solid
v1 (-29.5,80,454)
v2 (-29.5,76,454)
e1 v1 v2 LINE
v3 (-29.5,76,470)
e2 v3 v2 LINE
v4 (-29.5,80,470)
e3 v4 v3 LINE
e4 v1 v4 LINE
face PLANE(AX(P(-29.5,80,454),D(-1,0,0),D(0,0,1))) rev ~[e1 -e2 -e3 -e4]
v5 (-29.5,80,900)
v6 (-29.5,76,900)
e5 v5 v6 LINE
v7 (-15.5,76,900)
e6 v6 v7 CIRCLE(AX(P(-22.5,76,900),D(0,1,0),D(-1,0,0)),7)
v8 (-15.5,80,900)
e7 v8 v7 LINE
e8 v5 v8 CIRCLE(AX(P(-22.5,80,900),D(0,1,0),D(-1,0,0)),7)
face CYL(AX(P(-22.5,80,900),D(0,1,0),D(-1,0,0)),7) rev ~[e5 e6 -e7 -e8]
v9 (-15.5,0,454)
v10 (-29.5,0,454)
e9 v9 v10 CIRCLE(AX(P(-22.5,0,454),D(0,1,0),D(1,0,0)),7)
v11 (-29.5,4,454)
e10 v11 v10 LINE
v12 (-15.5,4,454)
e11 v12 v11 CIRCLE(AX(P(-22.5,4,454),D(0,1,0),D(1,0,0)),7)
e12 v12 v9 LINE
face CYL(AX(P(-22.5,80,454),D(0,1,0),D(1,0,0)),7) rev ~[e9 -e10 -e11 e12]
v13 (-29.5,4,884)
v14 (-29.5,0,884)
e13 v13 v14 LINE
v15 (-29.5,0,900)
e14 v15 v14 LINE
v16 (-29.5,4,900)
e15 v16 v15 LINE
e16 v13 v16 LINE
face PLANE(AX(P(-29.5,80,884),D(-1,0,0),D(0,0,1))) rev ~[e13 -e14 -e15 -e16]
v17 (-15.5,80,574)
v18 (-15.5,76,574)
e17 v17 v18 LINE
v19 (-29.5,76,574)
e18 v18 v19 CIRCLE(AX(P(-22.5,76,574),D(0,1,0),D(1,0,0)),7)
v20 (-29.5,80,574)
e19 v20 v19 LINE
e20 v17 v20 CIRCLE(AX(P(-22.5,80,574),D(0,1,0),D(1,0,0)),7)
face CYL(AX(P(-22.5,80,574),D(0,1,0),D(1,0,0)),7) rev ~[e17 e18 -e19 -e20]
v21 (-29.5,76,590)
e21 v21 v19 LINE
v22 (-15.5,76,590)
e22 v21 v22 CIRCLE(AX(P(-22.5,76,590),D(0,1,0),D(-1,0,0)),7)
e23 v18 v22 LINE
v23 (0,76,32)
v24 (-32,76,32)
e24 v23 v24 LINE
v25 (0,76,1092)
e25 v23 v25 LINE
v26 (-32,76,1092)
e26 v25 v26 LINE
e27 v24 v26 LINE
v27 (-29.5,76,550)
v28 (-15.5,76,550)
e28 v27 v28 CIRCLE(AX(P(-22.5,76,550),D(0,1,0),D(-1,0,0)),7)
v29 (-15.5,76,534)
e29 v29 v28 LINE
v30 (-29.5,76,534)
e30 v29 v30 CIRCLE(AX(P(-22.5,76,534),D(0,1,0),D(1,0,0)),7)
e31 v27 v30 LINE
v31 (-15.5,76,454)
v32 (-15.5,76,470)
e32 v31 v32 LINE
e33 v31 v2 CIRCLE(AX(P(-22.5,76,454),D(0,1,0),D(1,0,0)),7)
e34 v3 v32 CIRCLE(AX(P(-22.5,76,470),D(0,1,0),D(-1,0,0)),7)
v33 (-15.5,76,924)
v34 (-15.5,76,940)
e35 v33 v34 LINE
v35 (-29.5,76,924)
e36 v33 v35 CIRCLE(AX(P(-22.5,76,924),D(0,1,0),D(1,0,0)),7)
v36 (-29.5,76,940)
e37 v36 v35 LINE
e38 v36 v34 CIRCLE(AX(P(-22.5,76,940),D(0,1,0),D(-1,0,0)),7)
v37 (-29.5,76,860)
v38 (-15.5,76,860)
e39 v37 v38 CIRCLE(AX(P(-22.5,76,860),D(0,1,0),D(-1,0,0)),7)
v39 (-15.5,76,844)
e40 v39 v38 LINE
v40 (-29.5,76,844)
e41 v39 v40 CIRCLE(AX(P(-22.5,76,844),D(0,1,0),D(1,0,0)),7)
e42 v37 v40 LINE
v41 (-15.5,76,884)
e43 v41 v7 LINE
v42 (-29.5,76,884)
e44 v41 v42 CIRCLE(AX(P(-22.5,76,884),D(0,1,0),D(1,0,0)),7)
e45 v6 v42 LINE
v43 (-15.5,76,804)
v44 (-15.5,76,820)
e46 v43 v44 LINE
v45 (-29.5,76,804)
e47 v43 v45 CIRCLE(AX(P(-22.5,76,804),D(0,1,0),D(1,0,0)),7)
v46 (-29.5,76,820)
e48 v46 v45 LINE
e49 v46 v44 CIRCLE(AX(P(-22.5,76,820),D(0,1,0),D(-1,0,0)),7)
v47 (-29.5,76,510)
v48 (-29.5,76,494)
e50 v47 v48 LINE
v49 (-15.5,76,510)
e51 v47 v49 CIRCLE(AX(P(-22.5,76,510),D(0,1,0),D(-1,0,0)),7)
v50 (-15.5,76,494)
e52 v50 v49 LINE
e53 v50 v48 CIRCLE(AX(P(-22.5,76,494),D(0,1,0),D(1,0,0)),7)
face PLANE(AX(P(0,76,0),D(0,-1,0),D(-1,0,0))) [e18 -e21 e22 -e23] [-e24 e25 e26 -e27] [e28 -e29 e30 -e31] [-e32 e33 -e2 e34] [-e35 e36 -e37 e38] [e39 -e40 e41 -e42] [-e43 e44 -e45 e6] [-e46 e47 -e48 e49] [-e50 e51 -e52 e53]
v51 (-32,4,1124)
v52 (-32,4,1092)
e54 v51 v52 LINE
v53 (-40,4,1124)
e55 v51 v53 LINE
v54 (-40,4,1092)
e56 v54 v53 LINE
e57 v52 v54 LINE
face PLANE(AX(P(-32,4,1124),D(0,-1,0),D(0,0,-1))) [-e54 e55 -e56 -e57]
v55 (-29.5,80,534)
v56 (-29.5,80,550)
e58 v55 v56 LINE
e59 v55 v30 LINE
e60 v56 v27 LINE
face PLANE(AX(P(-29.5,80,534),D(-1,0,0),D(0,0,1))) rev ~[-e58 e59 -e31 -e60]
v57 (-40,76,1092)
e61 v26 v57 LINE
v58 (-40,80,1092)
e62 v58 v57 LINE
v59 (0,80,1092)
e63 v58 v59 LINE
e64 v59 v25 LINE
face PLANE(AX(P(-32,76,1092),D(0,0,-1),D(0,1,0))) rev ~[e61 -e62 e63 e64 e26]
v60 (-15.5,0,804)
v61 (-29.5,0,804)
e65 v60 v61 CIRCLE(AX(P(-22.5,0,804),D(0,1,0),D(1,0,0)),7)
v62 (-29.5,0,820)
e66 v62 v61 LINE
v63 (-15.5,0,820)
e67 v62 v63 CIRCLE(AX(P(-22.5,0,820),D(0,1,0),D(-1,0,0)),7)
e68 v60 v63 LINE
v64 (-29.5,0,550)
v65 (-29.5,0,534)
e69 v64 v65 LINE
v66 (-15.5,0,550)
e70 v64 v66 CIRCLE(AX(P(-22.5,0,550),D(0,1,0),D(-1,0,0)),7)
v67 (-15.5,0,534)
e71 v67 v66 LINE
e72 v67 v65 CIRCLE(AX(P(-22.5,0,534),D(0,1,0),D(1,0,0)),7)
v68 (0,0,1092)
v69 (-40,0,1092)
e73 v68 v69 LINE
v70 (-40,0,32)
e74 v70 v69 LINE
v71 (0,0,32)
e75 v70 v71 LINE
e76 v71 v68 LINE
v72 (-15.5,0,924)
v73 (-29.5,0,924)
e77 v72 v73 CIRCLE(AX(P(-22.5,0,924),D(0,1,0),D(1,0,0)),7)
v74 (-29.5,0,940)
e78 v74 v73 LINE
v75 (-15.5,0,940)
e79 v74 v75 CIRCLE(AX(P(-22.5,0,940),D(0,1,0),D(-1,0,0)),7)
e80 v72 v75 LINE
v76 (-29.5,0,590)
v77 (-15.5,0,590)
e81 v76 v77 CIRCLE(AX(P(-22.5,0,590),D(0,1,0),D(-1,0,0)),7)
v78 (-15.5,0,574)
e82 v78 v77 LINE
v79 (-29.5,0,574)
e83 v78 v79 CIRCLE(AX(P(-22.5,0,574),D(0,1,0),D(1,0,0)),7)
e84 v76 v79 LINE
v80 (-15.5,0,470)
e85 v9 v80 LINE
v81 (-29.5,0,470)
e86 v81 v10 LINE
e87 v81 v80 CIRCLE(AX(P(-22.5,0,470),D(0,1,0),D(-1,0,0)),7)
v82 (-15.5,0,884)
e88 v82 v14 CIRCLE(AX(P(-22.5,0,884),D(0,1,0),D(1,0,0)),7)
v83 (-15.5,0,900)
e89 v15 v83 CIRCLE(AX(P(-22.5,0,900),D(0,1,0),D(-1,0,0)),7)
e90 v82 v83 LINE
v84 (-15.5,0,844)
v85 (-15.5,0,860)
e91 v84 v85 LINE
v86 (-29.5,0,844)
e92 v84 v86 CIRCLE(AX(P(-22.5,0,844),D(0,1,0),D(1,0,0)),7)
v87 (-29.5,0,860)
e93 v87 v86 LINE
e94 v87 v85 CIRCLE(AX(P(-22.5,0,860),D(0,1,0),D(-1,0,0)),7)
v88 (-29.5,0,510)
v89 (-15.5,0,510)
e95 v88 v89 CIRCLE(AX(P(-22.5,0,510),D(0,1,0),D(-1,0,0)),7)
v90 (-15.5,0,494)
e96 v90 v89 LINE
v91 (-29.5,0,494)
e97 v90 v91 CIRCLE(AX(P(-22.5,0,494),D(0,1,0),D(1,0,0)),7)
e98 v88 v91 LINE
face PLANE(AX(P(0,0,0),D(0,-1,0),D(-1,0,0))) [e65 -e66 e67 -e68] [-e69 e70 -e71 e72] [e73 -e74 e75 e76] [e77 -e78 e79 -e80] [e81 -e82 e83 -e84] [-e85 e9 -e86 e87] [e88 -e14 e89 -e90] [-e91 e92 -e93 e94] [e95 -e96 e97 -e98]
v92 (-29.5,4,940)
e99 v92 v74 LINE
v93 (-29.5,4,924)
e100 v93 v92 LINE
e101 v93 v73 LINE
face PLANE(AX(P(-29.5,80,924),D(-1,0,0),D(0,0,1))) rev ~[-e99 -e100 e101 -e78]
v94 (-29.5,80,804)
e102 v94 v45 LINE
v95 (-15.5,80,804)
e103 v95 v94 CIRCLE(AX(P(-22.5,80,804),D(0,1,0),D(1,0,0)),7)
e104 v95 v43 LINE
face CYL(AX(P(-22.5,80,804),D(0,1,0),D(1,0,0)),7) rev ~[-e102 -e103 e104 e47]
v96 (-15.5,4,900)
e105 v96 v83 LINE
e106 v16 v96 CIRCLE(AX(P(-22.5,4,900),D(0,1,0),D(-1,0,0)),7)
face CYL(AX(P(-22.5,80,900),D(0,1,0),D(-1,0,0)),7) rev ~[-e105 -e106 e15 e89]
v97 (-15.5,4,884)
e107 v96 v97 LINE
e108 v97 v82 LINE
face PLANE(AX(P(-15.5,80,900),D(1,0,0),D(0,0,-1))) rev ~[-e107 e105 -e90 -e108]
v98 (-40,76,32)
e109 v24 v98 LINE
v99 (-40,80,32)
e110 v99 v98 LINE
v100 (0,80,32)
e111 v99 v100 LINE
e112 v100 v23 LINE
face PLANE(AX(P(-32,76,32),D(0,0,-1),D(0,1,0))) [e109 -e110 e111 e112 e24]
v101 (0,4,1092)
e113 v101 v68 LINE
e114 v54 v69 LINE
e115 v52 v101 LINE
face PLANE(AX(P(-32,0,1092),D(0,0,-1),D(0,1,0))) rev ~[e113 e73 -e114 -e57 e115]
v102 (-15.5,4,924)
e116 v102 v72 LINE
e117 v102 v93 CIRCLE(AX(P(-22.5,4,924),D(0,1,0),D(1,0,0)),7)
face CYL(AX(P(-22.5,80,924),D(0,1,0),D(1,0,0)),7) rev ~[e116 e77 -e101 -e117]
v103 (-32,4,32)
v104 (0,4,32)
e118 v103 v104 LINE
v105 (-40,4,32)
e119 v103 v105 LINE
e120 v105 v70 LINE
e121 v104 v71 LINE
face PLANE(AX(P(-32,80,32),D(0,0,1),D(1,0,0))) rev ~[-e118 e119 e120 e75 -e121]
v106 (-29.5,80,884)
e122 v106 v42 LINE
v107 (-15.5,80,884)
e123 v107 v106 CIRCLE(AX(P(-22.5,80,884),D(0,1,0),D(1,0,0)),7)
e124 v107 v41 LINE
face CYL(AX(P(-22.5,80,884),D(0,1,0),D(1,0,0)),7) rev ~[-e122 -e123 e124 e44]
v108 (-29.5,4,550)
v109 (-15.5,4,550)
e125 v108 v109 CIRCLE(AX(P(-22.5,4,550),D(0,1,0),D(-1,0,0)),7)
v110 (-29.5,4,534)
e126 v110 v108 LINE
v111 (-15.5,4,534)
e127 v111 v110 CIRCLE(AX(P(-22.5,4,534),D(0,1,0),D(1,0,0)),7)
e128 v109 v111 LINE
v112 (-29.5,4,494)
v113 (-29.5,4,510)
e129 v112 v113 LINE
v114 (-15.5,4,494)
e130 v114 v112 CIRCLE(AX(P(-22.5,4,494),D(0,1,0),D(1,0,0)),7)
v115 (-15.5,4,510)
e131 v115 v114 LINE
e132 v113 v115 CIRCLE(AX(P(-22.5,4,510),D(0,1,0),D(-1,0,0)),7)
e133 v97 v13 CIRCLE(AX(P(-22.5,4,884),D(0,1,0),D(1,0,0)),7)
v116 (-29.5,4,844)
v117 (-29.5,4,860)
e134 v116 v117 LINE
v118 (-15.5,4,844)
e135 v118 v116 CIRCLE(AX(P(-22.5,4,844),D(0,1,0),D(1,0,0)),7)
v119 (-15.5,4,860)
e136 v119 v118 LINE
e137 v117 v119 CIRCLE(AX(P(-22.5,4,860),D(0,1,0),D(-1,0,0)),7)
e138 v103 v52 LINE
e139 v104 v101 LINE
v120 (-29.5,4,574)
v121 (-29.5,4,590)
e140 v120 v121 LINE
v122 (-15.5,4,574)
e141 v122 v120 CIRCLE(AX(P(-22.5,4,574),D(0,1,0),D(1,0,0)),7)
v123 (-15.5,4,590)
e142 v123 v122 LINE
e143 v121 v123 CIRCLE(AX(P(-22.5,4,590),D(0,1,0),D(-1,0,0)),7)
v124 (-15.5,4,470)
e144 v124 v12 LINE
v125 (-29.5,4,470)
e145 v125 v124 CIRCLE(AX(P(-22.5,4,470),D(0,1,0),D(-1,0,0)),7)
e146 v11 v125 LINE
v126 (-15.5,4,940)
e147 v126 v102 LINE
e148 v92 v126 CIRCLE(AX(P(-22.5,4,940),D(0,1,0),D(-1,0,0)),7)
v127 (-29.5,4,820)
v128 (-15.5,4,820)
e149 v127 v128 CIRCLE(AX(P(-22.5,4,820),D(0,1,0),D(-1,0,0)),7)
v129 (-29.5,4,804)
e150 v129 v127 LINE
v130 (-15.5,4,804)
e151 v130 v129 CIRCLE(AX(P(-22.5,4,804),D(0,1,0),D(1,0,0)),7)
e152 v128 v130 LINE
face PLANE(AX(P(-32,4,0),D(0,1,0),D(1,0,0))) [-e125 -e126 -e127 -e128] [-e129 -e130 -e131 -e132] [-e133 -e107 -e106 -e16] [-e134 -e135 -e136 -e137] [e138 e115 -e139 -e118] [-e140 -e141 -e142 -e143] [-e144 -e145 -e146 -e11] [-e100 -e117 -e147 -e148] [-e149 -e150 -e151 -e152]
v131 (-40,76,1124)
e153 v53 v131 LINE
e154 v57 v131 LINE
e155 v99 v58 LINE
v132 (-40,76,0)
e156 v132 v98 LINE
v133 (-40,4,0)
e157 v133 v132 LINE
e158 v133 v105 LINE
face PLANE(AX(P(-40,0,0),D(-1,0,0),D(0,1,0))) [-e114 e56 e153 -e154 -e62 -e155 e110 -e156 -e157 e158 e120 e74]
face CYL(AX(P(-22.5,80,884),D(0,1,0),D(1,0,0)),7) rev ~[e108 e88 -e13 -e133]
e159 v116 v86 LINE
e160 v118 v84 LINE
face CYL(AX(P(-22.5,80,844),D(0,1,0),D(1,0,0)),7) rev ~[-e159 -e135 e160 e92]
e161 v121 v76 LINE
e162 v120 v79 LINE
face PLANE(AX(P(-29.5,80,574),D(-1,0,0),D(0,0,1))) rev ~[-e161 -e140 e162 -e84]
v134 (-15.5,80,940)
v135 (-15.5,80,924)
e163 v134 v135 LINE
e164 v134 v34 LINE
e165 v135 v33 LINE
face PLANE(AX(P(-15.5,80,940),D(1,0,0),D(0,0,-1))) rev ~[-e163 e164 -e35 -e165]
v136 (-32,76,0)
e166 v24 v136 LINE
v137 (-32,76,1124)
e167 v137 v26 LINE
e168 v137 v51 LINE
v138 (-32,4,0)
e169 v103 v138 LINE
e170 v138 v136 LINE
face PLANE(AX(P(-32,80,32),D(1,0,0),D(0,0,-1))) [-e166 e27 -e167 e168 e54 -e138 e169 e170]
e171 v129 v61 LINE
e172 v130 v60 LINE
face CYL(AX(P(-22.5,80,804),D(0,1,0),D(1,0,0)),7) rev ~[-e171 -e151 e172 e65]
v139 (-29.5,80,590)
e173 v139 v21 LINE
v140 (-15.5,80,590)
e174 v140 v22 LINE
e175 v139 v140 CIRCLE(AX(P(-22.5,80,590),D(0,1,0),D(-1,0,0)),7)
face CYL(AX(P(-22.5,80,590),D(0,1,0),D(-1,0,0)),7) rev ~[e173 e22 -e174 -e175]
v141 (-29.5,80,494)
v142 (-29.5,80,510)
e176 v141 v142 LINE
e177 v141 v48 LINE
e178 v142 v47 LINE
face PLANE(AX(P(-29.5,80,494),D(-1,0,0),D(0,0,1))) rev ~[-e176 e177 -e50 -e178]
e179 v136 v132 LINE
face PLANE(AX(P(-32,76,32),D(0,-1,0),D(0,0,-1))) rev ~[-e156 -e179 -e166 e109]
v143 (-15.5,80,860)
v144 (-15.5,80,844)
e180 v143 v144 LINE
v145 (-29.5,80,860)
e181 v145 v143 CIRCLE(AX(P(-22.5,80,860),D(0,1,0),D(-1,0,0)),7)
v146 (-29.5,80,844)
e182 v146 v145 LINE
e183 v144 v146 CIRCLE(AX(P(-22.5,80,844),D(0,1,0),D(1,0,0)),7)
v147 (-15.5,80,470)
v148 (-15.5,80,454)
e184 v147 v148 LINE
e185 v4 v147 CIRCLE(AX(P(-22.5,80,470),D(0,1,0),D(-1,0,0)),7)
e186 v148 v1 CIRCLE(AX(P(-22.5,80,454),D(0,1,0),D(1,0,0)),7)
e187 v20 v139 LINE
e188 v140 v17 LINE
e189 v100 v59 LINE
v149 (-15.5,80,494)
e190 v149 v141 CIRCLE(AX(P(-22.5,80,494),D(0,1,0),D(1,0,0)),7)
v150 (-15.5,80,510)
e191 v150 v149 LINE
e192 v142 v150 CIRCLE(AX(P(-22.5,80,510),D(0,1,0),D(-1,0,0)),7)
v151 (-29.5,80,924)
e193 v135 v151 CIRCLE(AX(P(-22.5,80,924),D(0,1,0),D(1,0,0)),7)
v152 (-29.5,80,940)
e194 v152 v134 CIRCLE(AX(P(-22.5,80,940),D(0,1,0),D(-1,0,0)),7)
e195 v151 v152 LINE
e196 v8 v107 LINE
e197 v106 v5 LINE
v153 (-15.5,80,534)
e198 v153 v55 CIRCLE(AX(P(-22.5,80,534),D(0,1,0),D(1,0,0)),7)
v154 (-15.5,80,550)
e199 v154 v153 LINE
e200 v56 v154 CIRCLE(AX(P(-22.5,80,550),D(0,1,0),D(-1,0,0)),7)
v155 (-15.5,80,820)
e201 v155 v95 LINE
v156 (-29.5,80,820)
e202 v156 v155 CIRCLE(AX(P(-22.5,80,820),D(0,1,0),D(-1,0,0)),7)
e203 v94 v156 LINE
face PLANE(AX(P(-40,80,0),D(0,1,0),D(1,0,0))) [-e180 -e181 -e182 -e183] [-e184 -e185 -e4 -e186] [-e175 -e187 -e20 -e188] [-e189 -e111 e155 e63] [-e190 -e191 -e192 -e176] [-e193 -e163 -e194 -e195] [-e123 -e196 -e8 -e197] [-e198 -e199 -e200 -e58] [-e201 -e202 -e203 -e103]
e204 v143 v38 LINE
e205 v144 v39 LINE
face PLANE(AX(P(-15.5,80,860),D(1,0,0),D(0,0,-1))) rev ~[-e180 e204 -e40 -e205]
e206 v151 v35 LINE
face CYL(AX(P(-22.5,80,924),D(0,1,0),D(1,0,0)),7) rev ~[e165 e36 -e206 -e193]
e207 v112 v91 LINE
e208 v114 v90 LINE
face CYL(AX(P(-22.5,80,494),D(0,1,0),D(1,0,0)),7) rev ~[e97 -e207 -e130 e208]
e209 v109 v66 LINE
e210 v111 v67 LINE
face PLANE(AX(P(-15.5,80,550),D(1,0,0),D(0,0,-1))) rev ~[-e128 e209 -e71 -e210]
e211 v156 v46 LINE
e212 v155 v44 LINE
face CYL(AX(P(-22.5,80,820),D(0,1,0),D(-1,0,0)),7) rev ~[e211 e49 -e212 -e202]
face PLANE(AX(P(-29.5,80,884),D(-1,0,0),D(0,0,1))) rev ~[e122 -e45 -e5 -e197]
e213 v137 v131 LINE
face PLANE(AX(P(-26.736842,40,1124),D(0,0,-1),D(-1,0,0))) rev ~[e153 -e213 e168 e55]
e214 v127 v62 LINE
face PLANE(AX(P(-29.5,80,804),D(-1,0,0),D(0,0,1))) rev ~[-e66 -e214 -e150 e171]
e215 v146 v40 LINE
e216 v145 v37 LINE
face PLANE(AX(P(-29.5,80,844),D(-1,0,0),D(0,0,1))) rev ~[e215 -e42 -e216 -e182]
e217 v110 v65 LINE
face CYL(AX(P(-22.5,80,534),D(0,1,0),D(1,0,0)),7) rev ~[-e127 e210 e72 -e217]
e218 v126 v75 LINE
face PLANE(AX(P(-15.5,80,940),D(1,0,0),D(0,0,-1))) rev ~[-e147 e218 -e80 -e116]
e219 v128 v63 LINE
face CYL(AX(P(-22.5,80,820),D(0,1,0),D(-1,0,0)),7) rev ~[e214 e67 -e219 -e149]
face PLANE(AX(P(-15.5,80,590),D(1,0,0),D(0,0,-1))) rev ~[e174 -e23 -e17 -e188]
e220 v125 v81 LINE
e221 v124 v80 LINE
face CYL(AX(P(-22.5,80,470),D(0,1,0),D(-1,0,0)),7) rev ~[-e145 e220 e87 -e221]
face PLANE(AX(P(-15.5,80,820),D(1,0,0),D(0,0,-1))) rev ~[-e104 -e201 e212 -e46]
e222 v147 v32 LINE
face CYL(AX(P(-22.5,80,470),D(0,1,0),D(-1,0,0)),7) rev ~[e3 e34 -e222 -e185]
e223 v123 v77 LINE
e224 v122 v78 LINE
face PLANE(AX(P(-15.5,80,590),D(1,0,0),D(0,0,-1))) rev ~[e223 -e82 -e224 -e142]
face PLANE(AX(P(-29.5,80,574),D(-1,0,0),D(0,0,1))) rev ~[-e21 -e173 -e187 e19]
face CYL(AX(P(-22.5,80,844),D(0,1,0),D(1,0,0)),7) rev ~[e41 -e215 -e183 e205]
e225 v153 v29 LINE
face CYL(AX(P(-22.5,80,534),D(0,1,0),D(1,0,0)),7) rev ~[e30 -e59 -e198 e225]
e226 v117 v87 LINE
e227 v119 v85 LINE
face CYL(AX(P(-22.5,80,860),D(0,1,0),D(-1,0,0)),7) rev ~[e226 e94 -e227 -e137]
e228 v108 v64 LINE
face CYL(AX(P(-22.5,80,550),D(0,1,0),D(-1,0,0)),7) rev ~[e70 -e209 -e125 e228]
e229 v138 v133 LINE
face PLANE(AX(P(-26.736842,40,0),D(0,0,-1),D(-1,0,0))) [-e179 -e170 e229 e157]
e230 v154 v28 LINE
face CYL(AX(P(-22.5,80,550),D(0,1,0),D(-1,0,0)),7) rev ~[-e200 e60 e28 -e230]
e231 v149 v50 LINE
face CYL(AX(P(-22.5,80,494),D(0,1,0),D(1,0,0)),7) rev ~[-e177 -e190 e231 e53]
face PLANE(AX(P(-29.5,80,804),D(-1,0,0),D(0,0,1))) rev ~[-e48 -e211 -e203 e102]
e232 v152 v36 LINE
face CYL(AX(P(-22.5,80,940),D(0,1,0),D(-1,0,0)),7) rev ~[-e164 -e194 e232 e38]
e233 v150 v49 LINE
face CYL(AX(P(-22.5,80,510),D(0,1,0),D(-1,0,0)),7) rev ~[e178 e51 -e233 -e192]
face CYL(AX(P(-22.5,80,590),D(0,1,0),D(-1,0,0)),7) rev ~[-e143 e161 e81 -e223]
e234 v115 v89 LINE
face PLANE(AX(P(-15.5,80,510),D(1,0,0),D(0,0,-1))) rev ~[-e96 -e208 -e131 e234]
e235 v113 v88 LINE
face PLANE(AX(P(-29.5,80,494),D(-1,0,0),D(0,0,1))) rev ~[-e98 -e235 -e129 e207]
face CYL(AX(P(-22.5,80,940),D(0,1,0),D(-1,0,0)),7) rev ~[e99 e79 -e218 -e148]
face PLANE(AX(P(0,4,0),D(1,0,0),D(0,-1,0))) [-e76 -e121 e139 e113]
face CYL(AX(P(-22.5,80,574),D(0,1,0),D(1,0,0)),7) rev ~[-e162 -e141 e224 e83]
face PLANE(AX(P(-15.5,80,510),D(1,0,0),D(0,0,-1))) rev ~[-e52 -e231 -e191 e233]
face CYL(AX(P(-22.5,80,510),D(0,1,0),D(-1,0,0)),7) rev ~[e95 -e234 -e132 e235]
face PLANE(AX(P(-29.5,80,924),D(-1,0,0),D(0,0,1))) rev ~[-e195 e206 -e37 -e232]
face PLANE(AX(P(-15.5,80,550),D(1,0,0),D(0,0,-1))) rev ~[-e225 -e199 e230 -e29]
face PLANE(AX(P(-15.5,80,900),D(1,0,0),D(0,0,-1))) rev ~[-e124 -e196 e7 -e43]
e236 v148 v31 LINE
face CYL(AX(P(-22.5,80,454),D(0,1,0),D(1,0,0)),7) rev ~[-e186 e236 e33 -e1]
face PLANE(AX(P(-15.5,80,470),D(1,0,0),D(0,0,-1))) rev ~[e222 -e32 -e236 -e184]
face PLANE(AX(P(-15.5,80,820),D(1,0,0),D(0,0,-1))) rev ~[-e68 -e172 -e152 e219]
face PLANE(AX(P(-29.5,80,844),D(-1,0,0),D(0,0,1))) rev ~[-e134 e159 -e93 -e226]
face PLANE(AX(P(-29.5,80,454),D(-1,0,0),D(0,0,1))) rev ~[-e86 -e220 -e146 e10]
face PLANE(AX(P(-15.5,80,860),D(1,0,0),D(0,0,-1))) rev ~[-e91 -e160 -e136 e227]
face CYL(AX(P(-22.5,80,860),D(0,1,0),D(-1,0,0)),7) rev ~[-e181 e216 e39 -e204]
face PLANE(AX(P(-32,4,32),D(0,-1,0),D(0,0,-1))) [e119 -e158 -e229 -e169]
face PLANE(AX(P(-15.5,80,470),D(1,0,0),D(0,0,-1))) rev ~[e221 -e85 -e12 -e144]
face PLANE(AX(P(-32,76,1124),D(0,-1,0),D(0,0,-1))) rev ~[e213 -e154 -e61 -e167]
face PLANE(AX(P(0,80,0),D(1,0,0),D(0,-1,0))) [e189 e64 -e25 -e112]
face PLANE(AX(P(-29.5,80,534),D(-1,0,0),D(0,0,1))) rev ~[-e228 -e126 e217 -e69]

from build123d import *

# Parameters (mm, degrees)
EXTRUDE1_DEPTH         = 1124
SKETCH2_W              = 32
SKETCH2_H              = 32
CUT_EXTRUDE1_DEPTH     = 1128.553102962
SKETCH3_W              = 32
SKETCH3_H              = 4
CUT_EXTRUDE2_DEPTH     = 1200
CUT_EXTRUDE3_DEPTH     = 1128.553102962
LPATTERN1_COUNT        = 4
LPATTERN1_PITCH        = 40
LPATTERN2_COUNT        = 2
LPATTERN2_PITCH        = 350
LPATTERN2_COPY_1_DEPTH = 1128.553102962
LPATTERN2_COPY_2_DEPTH = 1128.553102962
LPATTERN2_COPY_3_DEPTH = 1128.553102962


with BuildPart() as part:
    # Sketch1 → Extrude1 (new body)
    with BuildSketch(Plane.XY):
        Polygon((0, 0), (-40, 0), (-40, 80), (0, 80), (0, 76), (-32, 76), (-32, 4), (0, 4), align=None)
    extrude(amount=EXTRUDE1_DEPTH)

    # Sketch2 → Cut-Extrude1 (cut, through all)
    with BuildSketch(Plane(origin=(0, 80, 0), x_dir=(1, 0, 0), z_dir=(0, 1, 0))):
        with Locations((-16, -16)):
            Rectangle(SKETCH2_W, SKETCH2_H)
        with Locations((-16, -1108)):
            Rectangle(SKETCH2_W, SKETCH2_H)
    extrude(amount=-CUT_EXTRUDE1_DEPTH, mode=Mode.SUBTRACT)

    # Sketch3 → Cut-Extrude2 (cut)
    with BuildSketch(Plane(origin=(-32, 0, 0), x_dir=(0, 0, -1), z_dir=(1, 0, 0))):
        with Locations((-1108, 78)):
            Rectangle(SKETCH3_W, SKETCH3_H)
        with Locations((-1108, 2)):
            Rectangle(SKETCH3_W, SKETCH3_H)
        with Locations((-16, 78)):
            Rectangle(SKETCH3_W, SKETCH3_H)
        with Locations((-16, 2)):
            Rectangle(SKETCH3_W, SKETCH3_H)
    extrude(amount=-CUT_EXTRUDE2_DEPTH, mode=Mode.SUBTRACT)

    # Sketch4 → Cut-Extrude3 (cut, through all)
    with BuildSketch(Plane(origin=(0, 80, 0), x_dir=(1, 0, 0), z_dir=(0, 1, 0))):
        with BuildLine():
            Line((-29.5, -924), (-29.5, -940))
            ThreePointArc((-29.5, -940), (-22.5, -947), (-15.5, -940))
            Line((-15.5, -940), (-15.5, -924))
            ThreePointArc((-15.5, -924), (-22.5, -917), (-29.5, -924))
        make_face()
    cut_extrude3 = extrude(amount=-CUT_EXTRUDE3_DEPTH, mode=Mode.SUBTRACT)

    # LPattern1: Cut-Extrude3 ×4
    with Locations(*[(0, 0, -i * LPATTERN1_PITCH) for i in range(1, LPATTERN1_COUNT)]):
        add(cut_extrude3, mode=Mode.SUBTRACT)

    # LPattern2: Cut-Extrude3 ×2
    with Locations(*[(0, 0, -i * LPATTERN2_PITCH) for i in range(1, LPATTERN2_COUNT)]):
        add(cut_extrude3, mode=Mode.SUBTRACT)

    # LPattern2 copy 1 sketch → LPattern2 copy 1 (cut, through all)
    with BuildSketch(Plane(origin=(0, 80, -390), x_dir=(1, 0, 0), z_dir=(0, 1, 0))):
        with BuildLine():
            Line((-29.5, -924), (-29.5, -940))
            ThreePointArc((-29.5, -940), (-22.5, -947), (-15.5, -940))
            Line((-15.5, -940), (-15.5, -924))
            ThreePointArc((-15.5, -924), (-22.5, -917), (-29.5, -924))
        make_face()
    extrude(amount=-LPATTERN2_COPY_1_DEPTH, mode=Mode.SUBTRACT)

    # LPattern2 copy 2 sketch → LPattern2 copy 2 (cut, through all)
    with BuildSketch(Plane(origin=(0, 80, -430), x_dir=(1, 0, 0), z_dir=(0, 1, 0))):
        with BuildLine():
            Line((-29.5, -924), (-29.5, -940))
            ThreePointArc((-29.5, -940), (-22.5, -947), (-15.5, -940))
            Line((-15.5, -940), (-15.5, -924))
            ThreePointArc((-15.5, -924), (-22.5, -917), (-29.5, -924))
        make_face()
    extrude(amount=-LPATTERN2_COPY_2_DEPTH, mode=Mode.SUBTRACT)

    # LPattern2 copy 3 sketch → LPattern2 copy 3 (cut, through all)
    with BuildSketch(Plane(origin=(0, 80, -470), x_dir=(1, 0, 0), z_dir=(0, 1, 0))):
        with BuildLine():
            Line((-29.5, -924), (-29.5, -940))
            ThreePointArc((-29.5, -940), (-22.5, -947), (-15.5, -940))
            Line((-15.5, -940), (-15.5, -924))
            ThreePointArc((-15.5, -924), (-22.5, -917), (-29.5, -924))
        make_face()
    extrude(amount=-LPATTERN2_COPY_3_DEPTH, mode=Mode.SUBTRACT)


solid = part.part
